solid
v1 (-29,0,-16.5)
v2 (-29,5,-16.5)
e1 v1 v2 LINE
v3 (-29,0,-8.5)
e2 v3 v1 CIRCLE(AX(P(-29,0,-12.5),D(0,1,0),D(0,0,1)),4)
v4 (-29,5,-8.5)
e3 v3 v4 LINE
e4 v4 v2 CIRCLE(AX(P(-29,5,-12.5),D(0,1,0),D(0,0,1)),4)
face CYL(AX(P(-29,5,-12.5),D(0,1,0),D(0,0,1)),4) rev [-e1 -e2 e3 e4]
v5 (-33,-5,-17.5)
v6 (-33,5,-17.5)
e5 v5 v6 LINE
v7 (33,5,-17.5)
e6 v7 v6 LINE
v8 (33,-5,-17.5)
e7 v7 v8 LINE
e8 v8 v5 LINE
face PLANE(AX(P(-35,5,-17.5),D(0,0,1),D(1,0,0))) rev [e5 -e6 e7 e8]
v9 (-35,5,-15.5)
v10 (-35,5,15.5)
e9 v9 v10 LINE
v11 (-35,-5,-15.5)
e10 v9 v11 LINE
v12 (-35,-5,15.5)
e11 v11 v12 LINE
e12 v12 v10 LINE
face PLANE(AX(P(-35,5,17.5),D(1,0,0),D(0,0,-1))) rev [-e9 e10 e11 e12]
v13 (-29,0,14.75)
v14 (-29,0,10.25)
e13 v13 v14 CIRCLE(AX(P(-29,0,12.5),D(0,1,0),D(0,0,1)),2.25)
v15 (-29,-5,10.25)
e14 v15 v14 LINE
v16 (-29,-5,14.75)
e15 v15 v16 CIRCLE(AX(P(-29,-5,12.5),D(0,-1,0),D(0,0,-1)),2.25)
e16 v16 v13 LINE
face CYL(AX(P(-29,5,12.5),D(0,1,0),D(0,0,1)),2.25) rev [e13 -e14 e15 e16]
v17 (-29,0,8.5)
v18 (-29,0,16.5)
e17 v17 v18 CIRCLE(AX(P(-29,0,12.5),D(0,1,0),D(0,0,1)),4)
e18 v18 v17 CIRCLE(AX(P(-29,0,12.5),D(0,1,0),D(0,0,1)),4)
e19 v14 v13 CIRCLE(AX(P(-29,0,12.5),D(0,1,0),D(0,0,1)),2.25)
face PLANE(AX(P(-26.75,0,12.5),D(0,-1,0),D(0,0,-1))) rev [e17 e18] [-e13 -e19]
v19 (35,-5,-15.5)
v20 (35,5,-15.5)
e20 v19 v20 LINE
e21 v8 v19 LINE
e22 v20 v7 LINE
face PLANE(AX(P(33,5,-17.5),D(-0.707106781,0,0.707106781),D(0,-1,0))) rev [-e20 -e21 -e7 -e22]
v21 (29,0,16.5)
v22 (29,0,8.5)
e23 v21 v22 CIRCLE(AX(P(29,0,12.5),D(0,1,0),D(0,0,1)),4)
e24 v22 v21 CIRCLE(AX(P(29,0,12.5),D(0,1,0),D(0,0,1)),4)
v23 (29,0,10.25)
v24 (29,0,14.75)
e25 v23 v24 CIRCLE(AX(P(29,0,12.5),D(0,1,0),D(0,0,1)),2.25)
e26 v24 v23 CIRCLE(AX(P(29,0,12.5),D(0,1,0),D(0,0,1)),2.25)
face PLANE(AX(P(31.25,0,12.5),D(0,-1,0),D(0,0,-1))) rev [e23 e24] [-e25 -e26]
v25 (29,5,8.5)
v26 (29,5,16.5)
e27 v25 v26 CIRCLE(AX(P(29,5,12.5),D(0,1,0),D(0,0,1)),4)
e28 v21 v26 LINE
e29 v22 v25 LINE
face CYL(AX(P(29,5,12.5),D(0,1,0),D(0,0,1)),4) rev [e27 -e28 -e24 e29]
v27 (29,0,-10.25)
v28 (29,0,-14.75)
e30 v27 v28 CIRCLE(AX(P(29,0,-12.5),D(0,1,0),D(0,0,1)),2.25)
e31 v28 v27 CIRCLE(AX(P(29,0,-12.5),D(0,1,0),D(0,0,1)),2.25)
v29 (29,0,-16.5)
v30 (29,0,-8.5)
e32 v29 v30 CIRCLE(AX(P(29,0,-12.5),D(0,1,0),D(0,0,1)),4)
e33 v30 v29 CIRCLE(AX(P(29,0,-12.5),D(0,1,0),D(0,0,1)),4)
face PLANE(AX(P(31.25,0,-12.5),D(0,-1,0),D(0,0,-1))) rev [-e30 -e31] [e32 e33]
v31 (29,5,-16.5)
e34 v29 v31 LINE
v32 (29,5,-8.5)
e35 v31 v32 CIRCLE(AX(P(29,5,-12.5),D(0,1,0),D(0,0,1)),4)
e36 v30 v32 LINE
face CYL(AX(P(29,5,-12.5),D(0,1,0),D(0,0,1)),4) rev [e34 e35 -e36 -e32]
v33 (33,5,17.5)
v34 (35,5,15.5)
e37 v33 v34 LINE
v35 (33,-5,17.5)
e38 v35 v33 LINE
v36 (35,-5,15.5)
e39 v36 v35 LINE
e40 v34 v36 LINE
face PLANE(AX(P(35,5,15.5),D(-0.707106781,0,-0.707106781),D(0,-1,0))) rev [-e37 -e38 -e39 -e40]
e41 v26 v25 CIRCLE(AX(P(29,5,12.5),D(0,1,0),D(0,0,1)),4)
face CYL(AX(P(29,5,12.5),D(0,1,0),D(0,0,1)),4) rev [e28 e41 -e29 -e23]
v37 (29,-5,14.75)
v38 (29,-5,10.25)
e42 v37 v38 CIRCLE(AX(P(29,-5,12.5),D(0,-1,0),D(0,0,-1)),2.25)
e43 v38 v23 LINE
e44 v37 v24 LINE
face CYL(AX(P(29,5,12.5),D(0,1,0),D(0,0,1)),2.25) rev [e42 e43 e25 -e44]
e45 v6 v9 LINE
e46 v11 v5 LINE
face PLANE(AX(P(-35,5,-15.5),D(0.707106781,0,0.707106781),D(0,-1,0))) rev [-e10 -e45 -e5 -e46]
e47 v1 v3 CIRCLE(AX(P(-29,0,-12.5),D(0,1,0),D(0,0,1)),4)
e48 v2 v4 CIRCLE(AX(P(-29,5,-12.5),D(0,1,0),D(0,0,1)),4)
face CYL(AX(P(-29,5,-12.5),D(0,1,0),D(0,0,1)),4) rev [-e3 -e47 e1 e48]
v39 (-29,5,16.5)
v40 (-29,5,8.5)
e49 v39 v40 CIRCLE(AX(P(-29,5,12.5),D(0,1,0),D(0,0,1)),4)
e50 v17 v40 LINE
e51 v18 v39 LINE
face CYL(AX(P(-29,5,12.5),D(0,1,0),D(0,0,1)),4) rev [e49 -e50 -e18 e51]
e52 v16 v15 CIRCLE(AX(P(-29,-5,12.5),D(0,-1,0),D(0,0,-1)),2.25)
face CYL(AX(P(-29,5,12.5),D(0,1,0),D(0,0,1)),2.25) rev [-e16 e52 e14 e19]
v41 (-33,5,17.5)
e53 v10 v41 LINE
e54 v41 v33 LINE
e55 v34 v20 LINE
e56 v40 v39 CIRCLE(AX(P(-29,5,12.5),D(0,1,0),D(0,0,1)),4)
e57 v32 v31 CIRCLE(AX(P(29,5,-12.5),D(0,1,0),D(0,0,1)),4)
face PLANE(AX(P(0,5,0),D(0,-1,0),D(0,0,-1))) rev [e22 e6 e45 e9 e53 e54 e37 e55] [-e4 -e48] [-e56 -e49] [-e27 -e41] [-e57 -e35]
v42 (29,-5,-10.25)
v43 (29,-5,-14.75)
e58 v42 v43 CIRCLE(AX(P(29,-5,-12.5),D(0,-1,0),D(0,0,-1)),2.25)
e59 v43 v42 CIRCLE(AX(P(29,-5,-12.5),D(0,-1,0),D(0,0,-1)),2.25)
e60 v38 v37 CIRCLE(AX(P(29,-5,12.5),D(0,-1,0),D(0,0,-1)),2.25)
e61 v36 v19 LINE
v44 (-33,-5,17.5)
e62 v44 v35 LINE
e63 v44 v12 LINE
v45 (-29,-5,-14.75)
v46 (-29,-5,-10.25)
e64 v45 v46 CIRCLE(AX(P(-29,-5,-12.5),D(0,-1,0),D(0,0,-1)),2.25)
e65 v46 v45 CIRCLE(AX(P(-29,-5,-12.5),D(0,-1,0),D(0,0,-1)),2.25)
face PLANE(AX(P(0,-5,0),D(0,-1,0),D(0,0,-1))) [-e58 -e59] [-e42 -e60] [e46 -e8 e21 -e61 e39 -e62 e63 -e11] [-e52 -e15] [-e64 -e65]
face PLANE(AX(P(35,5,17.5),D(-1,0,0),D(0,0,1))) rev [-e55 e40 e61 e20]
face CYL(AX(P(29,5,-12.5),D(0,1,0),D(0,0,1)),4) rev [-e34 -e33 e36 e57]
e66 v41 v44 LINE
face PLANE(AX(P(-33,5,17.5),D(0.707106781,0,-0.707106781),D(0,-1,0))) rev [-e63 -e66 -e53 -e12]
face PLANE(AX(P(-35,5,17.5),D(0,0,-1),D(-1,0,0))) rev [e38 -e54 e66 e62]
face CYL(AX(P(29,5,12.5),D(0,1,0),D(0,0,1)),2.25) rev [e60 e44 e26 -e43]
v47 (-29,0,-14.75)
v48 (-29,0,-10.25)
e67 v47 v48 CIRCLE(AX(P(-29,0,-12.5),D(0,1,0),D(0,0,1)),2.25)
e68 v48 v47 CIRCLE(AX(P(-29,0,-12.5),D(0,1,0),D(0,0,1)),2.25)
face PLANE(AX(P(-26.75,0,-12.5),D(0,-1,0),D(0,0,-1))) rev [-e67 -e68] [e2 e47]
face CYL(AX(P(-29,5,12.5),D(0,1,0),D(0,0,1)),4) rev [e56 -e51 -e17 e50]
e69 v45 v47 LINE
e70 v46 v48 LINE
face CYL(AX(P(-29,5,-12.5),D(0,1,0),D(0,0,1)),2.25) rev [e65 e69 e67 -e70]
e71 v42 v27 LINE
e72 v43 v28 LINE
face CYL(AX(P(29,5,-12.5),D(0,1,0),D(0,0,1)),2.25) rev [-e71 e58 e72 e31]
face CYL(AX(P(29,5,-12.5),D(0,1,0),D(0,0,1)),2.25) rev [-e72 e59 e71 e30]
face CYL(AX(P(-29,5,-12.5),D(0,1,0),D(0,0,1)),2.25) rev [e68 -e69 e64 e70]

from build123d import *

# Parameters (mm, degrees)
SKETCH_1_W                   = 70
SKETCH_1_H                   = 35
EXTRUDE_1_DEPTH              = 5
CHAMFER_1_SIZE               = 2
HOLE_WIZARD_M4_1_D           = 4.5
HOLE_WIZARD_M4_1_CBORE_D     = 8
HOLE_WIZARD_M4_1_CBORE_DEPTH = 5


with BuildPart() as part:
    # 草图1 → 凸台-拉伸1 (new, symmetric)
    with BuildSketch(Plane(origin=(0, 0, 0), x_dir=(1, 0, 0), z_dir=(0, 1, 0))):
        Rectangle(SKETCH_1_W, SKETCH_1_H)
    extrude(amount=EXTRUDE_1_DEPTH, both=True)

    # 倒角1
    chamfer_1_edges = [part.edges().sort_by_distance(p)[0] for p in [
        (35, 0, 17.5),
        (-35, 0, 17.5),
        (-35, 0, -17.5),
        (35, 0, -17.5),
    ]]
    chamfer(chamfer_1_edges, length=CHAMFER_1_SIZE)

    # M4 六角圆柱头螺钉的柱形沉头孔1 (through all)
    with Locations(Plane(origin=(0, 5, 0), x_dir=(1, 0, 0), z_dir=(0, 1, 0))):
        with Locations((-29, 12.5), (-29, -12.5), (29, 12.5), (29, -12.5)):
            CounterBoreHole(HOLE_WIZARD_M4_1_D / 2, HOLE_WIZARD_M4_1_CBORE_D / 2, HOLE_WIZARD_M4_1_CBORE_DEPTH)


solid = part.part
